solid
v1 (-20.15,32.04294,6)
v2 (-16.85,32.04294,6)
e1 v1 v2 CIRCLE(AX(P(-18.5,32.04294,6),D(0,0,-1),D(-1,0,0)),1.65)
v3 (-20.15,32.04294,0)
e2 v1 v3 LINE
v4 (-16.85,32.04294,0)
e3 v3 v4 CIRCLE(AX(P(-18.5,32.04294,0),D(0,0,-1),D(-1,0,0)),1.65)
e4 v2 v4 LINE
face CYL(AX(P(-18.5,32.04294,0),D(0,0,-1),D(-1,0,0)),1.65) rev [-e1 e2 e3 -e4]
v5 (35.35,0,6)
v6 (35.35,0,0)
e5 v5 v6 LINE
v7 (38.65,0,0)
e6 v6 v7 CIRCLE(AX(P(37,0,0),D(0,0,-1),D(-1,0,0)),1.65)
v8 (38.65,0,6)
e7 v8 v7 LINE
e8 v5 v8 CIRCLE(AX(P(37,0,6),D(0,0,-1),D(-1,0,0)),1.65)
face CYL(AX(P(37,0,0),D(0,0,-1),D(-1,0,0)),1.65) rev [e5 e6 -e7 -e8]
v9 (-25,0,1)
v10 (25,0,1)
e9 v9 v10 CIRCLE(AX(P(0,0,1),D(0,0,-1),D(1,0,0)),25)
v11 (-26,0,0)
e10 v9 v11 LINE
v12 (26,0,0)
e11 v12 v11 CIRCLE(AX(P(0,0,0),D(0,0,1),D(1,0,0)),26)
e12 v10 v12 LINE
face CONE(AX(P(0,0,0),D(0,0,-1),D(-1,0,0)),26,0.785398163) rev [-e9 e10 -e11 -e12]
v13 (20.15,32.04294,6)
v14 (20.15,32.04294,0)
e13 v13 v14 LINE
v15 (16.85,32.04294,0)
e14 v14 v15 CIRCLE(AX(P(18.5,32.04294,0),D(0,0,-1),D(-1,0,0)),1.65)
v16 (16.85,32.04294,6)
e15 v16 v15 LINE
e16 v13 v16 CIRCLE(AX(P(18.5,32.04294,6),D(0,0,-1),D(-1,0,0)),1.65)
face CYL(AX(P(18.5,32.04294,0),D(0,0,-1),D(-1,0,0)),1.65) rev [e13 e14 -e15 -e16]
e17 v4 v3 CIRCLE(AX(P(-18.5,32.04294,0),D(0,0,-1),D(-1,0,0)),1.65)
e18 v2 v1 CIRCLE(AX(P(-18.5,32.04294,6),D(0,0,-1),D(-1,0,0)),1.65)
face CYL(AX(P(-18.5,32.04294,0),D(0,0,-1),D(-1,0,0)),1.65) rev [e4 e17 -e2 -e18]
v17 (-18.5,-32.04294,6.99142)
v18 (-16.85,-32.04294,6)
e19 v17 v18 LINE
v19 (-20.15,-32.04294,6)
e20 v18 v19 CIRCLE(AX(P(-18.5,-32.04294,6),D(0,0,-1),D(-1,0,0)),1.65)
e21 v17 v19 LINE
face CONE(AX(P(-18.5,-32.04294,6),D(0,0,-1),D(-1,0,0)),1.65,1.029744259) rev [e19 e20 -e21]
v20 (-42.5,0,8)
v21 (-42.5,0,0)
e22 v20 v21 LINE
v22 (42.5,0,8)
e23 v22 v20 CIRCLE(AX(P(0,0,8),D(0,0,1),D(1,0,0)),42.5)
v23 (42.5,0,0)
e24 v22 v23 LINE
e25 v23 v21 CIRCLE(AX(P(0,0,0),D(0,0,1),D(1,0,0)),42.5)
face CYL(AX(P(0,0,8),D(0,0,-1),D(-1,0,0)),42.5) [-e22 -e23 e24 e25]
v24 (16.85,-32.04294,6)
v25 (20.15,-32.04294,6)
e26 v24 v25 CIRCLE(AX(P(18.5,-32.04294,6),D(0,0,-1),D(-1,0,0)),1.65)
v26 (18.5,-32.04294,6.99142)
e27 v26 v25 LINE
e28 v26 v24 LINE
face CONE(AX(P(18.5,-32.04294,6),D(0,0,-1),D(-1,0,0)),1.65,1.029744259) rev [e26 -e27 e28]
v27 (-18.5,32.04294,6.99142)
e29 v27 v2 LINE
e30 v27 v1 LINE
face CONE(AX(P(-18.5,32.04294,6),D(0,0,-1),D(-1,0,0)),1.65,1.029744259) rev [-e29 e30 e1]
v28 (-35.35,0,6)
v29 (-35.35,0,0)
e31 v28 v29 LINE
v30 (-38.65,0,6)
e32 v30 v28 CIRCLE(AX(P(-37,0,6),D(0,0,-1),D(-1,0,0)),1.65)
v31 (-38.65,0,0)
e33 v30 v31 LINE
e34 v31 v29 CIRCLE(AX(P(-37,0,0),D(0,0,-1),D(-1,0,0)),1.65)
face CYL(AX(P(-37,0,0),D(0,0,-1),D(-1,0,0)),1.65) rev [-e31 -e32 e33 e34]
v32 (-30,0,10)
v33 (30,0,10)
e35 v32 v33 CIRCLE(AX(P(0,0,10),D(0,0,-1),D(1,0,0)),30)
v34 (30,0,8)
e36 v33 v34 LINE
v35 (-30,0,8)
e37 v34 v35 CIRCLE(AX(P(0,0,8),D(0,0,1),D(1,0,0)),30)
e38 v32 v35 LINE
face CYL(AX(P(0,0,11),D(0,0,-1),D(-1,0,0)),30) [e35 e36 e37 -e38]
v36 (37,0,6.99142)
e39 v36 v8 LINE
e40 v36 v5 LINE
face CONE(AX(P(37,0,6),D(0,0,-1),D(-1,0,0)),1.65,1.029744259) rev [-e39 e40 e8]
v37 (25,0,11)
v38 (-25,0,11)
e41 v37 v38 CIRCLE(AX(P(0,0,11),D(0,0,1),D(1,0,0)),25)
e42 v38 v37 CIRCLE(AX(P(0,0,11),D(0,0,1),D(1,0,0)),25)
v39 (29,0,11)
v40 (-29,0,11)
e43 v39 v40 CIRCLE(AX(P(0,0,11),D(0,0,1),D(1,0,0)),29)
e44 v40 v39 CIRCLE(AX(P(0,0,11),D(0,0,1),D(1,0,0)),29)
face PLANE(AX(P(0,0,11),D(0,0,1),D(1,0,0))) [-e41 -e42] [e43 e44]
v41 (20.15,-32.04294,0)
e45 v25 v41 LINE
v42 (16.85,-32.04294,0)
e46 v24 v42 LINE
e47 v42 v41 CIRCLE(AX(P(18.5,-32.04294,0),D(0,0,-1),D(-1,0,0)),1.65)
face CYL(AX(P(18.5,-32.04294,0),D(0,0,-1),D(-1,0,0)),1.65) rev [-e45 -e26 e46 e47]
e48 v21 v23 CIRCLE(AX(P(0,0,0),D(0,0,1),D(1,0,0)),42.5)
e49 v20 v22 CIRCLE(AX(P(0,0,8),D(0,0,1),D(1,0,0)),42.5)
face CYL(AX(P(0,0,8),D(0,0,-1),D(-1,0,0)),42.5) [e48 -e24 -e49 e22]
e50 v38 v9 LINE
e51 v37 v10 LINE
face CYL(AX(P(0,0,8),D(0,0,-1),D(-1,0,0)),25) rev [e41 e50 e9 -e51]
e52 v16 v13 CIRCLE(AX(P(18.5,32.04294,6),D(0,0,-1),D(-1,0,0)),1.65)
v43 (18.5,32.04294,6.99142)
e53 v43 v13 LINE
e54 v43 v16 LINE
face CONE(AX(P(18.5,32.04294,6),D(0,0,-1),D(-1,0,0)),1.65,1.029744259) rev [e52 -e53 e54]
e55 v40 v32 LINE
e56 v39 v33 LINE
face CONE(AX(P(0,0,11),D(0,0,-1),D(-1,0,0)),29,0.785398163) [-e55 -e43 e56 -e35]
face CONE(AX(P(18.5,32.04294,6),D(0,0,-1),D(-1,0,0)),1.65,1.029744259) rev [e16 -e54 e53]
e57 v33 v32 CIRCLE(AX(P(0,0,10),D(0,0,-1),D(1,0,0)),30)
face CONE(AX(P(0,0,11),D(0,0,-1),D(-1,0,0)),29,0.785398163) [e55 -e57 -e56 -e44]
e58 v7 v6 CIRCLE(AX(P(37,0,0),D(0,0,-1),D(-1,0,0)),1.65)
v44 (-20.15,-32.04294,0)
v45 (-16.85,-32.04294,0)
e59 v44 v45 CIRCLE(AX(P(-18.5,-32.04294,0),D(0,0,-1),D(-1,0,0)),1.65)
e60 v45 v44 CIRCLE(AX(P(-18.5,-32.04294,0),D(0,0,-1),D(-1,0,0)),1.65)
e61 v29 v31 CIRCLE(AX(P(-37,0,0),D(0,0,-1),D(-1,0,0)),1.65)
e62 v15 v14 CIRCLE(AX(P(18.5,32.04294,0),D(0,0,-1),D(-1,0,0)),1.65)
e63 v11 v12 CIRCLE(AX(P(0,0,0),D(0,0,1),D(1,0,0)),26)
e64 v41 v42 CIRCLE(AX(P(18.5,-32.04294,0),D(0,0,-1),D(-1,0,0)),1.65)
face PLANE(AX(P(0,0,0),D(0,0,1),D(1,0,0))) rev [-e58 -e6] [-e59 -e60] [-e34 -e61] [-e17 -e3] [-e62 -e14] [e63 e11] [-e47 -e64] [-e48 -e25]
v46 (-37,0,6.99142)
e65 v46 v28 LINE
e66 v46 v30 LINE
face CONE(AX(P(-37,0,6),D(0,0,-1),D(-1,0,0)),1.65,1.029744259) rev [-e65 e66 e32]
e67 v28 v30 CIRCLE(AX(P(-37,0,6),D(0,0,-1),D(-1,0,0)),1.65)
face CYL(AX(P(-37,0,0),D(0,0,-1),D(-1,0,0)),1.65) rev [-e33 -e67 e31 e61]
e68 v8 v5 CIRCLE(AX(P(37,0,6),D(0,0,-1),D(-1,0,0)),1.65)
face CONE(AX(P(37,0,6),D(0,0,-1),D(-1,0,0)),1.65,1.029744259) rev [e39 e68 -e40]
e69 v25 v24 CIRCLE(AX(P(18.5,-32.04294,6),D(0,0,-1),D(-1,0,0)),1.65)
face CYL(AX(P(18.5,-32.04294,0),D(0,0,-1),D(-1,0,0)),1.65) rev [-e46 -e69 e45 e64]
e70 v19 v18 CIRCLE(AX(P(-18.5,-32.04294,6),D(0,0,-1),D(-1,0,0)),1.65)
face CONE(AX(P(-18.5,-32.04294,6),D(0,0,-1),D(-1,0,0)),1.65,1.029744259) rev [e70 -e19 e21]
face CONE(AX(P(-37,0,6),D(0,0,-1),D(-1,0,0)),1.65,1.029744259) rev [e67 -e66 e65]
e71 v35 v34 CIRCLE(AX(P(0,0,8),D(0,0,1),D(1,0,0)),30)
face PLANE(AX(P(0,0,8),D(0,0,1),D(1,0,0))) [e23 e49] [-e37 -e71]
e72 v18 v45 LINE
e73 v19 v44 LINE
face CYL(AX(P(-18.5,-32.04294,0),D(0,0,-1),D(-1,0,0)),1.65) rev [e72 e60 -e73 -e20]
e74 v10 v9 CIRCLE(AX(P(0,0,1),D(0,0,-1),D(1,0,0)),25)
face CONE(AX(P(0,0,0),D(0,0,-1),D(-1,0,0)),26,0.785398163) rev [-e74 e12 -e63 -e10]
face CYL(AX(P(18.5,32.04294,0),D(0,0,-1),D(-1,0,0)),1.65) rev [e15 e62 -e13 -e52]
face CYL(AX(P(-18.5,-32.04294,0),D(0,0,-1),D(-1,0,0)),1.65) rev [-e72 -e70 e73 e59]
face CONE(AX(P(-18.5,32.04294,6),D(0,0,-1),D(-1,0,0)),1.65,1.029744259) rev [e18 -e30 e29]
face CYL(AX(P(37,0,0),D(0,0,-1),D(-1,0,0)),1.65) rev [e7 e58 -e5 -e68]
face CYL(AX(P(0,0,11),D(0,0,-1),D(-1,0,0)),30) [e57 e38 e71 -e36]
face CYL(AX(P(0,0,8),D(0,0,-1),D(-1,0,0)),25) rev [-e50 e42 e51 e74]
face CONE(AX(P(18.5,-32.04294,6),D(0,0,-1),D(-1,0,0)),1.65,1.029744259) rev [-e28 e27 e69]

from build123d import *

# Parameters (mm, degrees)
SKETCH1_R             = 42.5
SKETCH1_R_2           = 25
BOSS_EXTRUDE1_DEPTH   = 8
SKETCH2_R             = 30
SKETCH2_R_2           = 25
BOSS_EXTRUDE2_DEPTH   = 3
CHAMFER1_SIZE         = 1
M4_TAPPED_HOLE1_D     = 3.3
M4_TAPPED_HOLE1_DEPTH = 6
M4_TAPPED_HOLE1_TIP   = 0.991420021


with BuildPart() as part:
    # Sketch1 → Boss-Extrude1 (new body)
    with BuildSketch(Plane.XY):
        Circle(SKETCH1_R)
        Circle(SKETCH1_R_2, mode=Mode.SUBTRACT)
    extrude(amount=BOSS_EXTRUDE1_DEPTH)

    # Sketch2 → Boss-Extrude2 (add)
    with BuildSketch(Plane.XY.offset(8)):
        Circle(SKETCH2_R)
        Circle(SKETCH2_R_2, mode=Mode.SUBTRACT)
    extrude(amount=BOSS_EXTRUDE2_DEPTH)

    # Chamfer1
    chamfer1_edges = [part.edges().sort_by_distance(p)[0] for p in [
        (-30, 0, 11),
        (-25, 0, 0),
    ]]
    chamfer(chamfer1_edges, length=CHAMFER1_SIZE)

    # M4 Tapped Hole1
    with Locations(Plane(origin=(18.5, 32.04293994, 0), x_dir=(-1, 0, 0), z_dir=(0, 0, -1))):
        with Locations((0, 0), (37, 0), (55.5, -32.04293994), (37, -64.08587988), (0, -64.08587988), (-18.5, -32.04293994)):
            Hole(M4_TAPPED_HOLE1_D / 2, depth=M4_TAPPED_HOLE1_DEPTH)
            with Locations((0, 0, -(M4_TAPPED_HOLE1_DEPTH + M4_TAPPED_HOLE1_TIP / 2))):  # 118° drill point
                Cone(0, M4_TAPPED_HOLE1_D / 2, M4_TAPPED_HOLE1_TIP, mode=Mode.SUBTRACT)


solid = part.part
